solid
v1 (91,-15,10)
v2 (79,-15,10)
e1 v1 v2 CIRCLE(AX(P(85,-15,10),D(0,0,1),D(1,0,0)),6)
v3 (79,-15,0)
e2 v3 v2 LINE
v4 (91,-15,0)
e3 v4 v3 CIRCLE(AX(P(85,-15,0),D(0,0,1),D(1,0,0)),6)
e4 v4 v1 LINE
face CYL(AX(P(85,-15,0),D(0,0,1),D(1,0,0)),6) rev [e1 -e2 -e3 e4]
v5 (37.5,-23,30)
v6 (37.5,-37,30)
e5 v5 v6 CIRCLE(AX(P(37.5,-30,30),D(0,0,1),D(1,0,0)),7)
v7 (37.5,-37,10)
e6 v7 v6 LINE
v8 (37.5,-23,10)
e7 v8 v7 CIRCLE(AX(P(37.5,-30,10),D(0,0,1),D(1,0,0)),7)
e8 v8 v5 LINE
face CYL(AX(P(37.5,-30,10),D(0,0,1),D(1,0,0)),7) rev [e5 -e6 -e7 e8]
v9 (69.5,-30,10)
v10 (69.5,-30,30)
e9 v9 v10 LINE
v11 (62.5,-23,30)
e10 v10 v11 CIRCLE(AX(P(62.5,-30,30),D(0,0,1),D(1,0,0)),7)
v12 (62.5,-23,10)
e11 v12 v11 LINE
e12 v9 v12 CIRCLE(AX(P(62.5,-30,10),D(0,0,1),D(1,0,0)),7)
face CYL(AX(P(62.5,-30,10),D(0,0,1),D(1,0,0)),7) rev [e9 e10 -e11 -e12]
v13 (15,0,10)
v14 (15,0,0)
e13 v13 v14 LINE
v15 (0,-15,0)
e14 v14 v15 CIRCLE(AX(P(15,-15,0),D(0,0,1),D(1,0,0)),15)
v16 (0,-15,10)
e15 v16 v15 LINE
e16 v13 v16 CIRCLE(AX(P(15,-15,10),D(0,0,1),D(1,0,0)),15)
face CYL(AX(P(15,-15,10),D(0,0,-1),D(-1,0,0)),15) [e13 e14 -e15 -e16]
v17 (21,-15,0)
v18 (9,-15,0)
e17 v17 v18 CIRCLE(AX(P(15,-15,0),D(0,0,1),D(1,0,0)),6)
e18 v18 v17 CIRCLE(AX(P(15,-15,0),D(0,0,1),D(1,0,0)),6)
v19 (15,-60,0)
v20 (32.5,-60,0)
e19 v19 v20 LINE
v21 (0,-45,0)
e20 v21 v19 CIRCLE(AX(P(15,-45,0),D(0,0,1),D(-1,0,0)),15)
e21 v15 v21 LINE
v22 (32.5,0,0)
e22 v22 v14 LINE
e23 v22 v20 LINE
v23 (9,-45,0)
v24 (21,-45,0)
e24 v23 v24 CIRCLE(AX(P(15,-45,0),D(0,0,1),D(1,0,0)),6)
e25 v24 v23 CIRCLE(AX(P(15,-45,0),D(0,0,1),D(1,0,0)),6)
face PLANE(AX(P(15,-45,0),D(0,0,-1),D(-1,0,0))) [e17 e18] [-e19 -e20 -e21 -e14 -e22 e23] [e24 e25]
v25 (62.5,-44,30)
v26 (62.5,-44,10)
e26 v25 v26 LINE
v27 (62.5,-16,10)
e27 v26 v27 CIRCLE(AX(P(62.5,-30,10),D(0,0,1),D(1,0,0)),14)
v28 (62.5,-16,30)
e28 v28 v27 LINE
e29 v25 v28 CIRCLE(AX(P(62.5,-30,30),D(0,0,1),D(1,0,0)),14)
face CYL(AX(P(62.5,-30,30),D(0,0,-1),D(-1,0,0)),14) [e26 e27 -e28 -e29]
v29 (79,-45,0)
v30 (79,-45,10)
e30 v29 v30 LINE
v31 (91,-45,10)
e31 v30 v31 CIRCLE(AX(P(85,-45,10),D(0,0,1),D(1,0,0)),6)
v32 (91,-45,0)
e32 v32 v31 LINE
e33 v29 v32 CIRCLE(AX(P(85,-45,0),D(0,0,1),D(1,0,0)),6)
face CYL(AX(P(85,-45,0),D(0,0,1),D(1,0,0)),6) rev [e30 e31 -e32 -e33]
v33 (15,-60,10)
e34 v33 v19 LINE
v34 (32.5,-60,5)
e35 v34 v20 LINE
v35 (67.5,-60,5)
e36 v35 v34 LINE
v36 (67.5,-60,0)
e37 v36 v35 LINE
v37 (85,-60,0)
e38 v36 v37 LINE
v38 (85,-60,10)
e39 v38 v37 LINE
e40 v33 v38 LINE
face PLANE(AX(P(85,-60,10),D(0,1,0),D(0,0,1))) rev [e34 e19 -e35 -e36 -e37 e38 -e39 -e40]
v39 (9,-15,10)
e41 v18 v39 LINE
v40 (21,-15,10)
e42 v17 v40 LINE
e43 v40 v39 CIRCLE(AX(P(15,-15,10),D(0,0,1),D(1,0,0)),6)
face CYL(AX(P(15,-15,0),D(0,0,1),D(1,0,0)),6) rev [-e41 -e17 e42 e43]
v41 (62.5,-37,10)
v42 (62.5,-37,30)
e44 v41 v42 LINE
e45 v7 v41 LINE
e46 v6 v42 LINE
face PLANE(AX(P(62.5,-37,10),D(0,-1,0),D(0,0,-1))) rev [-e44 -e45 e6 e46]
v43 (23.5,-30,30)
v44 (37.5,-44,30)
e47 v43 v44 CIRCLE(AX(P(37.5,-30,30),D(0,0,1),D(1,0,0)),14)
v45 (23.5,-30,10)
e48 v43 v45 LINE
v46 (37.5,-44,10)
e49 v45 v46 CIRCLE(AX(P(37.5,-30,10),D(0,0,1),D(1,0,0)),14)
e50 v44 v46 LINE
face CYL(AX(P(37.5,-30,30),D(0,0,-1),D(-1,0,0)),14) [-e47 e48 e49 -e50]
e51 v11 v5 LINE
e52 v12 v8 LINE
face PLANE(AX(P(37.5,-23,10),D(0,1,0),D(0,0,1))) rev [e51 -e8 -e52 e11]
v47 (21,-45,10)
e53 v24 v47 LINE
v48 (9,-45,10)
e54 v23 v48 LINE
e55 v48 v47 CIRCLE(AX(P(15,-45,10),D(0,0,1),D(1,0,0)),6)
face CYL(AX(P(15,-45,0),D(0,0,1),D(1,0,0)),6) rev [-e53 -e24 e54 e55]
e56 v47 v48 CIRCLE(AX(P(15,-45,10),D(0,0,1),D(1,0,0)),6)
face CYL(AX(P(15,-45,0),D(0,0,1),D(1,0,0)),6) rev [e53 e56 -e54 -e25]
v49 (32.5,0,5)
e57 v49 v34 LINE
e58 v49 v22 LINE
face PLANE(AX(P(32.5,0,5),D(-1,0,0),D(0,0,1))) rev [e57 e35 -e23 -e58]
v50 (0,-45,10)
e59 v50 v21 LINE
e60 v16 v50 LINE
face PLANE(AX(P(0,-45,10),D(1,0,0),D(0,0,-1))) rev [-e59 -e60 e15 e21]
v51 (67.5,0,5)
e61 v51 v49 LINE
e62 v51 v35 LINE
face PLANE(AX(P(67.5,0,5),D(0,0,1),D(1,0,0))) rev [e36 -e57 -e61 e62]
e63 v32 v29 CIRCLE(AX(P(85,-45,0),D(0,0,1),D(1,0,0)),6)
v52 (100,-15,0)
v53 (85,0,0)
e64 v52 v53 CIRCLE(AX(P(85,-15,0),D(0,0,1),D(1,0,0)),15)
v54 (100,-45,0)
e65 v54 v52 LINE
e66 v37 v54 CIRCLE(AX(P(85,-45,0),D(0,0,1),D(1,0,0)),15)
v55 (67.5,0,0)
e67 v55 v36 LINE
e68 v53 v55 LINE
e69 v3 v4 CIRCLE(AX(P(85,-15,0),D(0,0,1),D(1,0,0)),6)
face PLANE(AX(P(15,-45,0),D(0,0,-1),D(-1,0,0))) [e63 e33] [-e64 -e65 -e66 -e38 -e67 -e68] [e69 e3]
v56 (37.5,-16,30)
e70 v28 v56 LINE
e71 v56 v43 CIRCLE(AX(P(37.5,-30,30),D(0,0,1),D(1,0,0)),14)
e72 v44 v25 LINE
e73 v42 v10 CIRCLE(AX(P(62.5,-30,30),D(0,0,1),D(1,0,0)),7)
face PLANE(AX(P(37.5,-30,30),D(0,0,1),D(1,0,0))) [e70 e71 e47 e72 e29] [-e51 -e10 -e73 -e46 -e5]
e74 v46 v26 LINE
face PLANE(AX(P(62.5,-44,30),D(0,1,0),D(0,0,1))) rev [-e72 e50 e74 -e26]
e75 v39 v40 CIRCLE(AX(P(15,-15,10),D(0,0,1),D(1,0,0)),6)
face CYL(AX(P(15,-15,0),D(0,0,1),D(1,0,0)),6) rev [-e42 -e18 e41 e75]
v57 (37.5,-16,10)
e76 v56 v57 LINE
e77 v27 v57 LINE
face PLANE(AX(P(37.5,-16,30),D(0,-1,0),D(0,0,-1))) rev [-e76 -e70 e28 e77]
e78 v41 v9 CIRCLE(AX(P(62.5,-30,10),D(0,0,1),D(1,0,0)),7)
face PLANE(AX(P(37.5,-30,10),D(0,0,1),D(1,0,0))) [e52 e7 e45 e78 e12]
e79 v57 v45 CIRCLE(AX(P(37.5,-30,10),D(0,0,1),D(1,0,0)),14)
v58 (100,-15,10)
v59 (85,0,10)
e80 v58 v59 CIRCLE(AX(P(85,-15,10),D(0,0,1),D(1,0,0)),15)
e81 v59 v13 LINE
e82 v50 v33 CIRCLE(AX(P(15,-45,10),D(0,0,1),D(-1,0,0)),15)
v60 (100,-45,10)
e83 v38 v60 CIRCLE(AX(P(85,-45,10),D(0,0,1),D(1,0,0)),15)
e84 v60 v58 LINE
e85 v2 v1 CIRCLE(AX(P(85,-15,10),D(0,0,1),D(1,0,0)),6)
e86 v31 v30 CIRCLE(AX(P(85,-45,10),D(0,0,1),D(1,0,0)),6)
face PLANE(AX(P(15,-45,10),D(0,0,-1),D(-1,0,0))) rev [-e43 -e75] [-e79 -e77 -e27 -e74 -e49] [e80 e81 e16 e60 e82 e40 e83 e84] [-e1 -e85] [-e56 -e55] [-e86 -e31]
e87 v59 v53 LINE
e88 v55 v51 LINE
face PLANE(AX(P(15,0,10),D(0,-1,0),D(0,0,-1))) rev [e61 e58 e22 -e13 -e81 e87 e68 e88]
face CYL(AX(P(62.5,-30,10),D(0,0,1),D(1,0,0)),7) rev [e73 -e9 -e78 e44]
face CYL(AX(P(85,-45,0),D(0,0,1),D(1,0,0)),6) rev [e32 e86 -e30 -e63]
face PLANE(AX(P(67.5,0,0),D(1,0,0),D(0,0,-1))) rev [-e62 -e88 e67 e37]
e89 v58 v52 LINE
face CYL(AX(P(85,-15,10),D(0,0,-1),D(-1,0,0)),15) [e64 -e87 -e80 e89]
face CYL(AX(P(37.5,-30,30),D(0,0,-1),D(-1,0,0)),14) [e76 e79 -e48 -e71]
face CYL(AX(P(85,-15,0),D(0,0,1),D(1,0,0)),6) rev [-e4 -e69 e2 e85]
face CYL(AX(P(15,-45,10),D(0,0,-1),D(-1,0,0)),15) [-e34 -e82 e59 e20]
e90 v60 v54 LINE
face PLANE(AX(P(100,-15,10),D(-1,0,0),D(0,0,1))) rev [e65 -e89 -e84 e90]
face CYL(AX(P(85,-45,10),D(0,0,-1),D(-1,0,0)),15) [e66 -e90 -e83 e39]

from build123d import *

# Parameters (mm, degrees)
BASE_PLATE_DEPTH        = 10
MOUNTING_HOLES_SKETCH_R = 6
MOUNTING_HOLES_4X_DEPTH = 10
SLOT_BOSS_DEPTH         = 20
SLOT_THROUGH_CUT_DEPTH  = 20
BACK_CHANNEL_CUT_DEPTH  = 60


with BuildPart() as part:
    # Base Plate Sketch → Base Plate (new body)
    with BuildSketch(Plane.XY):
        with BuildLine():
            Line((15, 0), (85, 0))
            ThreePointArc((85, 0), (95.606601718, -4.393398282), (100, -15))
            Line((100, -15), (100, -45))
            ThreePointArc((100, -45), (95.606601718, -55.606601718), (85, -60))
            Line((85, -60), (15, -60))
            ThreePointArc((15, -60), (4.393398282, -55.606601718), (0, -45))
            Line((0, -45), (0, -15))
            ThreePointArc((0, -15), (4.393398282, -4.393398282), (15, 0))
        make_face()
    extrude(amount=BASE_PLATE_DEPTH)

    # Mounting Holes Sketch → Mounting Holes 4x (cut)
    with BuildSketch(Plane.XY.offset(10)):
        with Locations((15, -15)):
            Circle(MOUNTING_HOLES_SKETCH_R)
        with Locations((85, -15)):
            Circle(MOUNTING_HOLES_SKETCH_R)
        with Locations((85, -45)):
            Circle(MOUNTING_HOLES_SKETCH_R)
        with Locations((15, -45)):
            Circle(MOUNTING_HOLES_SKETCH_R)
    extrude(amount=-MOUNTING_HOLES_4X_DEPTH, mode=Mode.SUBTRACT)

    # Slot Boss Sketch → Slot Boss (add)
    with BuildSketch(Plane.XY.offset(10)):
        with BuildLine():
            Line((37.5, -16), (62.5, -16))
            ThreePointArc((62.5, -16), (76.5, -30), (62.5, -44))
            Line((62.5, -44), (37.5, -44))
            ThreePointArc((37.5, -44), (23.5, -30), (37.5, -16))
        make_face()
    extrude(amount=SLOT_BOSS_DEPTH)

    # Slot Cut Sketch → Slot Through Cut (cut)
    with BuildSketch(Plane.XY.offset(30)):
        with BuildLine():
            Line((37.5, -23), (62.5, -23))
            ThreePointArc((62.5, -23), (69.5, -30), (62.5, -37))
            Line((62.5, -37), (37.5, -37))
            ThreePointArc((37.5, -37), (30.5, -30), (37.5, -23))
        make_face()
    extrude(amount=-SLOT_THROUGH_CUT_DEPTH, mode=Mode.SUBTRACT)

    # Back Channel Sketch → Back Channel Cut (cut)
    with BuildSketch(Plane.XZ.offset(60)):
        Polygon((50, 0), (67.5, 0), (67.5, 5), (32.5, 5), (32.5, 0), align=None)
    extrude(amount=-BACK_CHANNEL_CUT_DEPTH, mode=Mode.SUBTRACT)


solid = part.part
